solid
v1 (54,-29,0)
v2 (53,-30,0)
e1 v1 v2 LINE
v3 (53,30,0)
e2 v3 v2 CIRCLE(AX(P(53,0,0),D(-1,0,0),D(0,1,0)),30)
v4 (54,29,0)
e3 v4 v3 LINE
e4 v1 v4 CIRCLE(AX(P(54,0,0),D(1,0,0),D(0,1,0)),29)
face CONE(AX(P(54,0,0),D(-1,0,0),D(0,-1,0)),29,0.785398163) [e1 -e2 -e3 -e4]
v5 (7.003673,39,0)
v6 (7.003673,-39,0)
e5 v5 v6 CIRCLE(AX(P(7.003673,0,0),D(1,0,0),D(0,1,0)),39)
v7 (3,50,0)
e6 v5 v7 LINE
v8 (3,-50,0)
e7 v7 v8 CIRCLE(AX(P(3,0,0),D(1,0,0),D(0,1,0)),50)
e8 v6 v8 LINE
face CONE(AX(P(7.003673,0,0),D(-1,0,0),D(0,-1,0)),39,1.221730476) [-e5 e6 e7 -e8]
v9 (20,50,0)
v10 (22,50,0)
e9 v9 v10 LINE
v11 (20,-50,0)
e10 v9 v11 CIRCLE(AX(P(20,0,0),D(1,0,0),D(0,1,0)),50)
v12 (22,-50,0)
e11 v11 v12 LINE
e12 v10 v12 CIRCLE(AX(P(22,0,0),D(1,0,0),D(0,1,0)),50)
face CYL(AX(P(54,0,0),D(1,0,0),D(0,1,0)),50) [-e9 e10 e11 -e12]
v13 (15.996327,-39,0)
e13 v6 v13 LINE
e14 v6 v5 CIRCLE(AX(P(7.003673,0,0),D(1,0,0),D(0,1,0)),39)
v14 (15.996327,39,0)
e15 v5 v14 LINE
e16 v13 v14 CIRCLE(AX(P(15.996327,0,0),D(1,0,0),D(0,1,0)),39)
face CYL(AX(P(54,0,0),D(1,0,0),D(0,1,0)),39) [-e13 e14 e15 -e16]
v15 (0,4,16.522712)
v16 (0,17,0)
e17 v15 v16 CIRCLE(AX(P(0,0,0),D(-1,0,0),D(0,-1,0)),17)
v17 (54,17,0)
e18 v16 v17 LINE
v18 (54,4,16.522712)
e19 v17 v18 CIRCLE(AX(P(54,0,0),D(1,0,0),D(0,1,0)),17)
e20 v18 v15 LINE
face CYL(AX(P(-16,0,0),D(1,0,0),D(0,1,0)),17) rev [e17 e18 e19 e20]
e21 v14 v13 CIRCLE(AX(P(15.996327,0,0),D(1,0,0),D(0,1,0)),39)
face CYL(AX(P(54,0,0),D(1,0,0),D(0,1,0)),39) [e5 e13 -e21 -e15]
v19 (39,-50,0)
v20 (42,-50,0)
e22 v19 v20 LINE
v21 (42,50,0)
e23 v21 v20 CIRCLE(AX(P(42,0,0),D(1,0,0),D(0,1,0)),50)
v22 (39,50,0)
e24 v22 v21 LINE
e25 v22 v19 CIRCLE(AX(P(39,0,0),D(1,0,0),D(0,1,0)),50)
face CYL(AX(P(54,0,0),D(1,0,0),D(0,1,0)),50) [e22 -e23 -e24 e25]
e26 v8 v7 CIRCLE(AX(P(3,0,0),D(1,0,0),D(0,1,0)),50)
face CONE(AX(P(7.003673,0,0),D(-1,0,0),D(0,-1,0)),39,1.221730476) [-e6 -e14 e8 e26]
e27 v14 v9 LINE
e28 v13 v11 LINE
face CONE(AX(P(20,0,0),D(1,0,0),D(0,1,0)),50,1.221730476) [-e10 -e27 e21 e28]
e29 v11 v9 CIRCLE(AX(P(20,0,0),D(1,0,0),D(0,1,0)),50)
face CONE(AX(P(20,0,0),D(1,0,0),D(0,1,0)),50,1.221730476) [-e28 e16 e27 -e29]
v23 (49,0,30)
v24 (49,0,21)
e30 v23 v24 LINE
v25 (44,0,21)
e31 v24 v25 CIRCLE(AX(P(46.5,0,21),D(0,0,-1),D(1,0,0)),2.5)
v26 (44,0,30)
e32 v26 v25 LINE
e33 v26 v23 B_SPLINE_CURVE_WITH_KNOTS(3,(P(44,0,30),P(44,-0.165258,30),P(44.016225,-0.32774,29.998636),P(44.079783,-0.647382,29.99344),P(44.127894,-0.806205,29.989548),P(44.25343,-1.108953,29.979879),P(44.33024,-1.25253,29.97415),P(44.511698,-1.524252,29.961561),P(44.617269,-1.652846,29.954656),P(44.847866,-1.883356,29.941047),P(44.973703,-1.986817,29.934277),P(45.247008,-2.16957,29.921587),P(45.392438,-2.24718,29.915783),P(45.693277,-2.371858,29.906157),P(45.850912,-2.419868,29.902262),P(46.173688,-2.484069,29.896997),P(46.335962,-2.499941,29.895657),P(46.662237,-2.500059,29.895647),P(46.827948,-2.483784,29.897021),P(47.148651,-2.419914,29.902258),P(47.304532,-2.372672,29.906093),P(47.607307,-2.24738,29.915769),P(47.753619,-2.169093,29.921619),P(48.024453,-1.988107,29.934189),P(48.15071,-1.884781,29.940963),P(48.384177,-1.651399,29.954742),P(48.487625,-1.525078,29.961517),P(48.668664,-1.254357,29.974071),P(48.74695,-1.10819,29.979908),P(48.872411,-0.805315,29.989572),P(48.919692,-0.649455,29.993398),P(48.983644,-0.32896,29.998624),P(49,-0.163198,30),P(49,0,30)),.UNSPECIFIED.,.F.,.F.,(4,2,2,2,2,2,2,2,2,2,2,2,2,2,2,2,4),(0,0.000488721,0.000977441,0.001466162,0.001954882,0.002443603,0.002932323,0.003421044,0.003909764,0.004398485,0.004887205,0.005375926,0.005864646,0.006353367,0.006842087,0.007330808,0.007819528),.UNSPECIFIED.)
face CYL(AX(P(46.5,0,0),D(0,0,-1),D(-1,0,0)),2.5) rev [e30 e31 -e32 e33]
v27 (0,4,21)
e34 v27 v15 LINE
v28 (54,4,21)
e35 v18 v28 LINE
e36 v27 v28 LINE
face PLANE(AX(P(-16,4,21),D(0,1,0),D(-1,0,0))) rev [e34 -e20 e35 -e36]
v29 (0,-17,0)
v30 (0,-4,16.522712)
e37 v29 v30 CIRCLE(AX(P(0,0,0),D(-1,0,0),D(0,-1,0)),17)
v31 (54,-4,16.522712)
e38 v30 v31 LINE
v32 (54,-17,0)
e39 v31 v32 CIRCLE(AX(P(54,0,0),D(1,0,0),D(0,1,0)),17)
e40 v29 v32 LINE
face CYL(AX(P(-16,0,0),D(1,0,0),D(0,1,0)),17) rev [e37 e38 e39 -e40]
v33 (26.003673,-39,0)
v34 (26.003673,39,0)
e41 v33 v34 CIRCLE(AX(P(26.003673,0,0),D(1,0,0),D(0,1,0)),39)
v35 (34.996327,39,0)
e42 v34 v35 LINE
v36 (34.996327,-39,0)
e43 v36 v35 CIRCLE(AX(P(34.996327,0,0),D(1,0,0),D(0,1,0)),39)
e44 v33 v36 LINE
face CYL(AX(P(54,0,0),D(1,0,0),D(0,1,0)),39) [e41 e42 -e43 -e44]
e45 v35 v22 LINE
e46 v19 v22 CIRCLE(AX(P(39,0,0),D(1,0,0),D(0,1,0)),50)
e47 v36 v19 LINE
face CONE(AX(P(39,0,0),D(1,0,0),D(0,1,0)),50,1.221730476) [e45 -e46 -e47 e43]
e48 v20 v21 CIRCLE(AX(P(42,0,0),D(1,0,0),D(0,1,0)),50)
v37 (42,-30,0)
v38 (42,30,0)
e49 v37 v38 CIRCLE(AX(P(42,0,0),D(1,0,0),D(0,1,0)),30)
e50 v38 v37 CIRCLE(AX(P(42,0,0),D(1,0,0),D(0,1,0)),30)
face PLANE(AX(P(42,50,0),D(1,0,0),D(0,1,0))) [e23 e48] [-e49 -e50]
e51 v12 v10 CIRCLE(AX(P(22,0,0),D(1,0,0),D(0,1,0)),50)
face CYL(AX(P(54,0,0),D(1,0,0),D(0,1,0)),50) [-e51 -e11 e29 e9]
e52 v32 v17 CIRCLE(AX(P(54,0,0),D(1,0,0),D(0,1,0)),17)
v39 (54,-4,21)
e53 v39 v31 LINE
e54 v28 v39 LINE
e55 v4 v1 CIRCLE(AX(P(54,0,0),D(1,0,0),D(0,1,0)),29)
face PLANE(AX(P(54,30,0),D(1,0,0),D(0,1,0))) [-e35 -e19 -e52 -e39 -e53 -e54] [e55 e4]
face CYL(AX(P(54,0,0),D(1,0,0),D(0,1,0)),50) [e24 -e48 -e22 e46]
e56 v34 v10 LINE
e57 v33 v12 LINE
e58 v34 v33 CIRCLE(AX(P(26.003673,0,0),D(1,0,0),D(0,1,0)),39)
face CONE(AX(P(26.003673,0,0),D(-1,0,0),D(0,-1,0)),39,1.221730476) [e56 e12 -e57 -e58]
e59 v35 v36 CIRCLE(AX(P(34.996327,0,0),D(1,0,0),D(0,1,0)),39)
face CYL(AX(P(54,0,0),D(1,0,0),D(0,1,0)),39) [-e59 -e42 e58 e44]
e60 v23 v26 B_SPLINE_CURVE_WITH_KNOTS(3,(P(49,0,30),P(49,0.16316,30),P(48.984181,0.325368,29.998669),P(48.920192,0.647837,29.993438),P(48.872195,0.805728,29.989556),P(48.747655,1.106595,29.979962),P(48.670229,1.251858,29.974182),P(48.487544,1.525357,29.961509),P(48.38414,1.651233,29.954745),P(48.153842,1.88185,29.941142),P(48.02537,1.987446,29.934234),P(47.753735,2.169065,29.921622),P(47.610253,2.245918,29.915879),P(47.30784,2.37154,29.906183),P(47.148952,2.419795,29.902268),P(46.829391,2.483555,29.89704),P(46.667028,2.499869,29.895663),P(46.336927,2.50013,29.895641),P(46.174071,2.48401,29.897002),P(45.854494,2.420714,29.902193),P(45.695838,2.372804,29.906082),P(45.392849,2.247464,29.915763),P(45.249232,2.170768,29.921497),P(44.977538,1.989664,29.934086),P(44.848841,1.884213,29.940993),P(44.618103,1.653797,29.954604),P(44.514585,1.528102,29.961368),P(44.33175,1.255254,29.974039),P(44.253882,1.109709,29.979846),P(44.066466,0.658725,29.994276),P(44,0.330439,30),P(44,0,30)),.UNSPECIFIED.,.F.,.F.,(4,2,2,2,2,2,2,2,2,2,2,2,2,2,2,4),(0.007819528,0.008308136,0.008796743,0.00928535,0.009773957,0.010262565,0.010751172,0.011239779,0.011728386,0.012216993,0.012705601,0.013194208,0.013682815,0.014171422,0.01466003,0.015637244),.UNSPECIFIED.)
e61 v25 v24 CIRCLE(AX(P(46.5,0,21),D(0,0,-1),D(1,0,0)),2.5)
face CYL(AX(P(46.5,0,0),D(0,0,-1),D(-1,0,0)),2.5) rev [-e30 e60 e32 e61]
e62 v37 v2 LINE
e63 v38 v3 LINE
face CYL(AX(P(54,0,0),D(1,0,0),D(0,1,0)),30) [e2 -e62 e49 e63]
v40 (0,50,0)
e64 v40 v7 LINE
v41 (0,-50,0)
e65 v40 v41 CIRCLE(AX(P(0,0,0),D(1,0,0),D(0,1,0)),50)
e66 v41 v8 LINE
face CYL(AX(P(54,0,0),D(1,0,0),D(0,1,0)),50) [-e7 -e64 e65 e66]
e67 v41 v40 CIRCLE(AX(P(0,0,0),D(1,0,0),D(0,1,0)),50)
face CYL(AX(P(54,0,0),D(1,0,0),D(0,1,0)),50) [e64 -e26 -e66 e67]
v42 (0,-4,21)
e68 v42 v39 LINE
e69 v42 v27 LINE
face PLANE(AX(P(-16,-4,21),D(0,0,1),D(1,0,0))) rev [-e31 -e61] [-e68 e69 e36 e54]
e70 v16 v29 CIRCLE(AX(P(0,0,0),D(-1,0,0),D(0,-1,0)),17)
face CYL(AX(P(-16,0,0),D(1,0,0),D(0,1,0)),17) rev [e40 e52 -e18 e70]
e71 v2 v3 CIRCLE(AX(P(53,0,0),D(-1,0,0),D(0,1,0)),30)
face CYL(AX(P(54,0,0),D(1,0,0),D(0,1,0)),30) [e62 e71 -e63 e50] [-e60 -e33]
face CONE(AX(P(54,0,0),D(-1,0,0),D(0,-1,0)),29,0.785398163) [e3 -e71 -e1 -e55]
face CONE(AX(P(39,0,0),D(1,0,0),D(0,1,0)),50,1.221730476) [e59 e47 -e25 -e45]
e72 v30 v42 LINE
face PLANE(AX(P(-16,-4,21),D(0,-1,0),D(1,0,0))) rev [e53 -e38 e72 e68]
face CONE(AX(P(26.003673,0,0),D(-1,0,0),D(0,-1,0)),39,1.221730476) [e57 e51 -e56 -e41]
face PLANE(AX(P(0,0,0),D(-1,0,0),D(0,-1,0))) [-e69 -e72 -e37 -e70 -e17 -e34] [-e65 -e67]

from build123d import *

# Parameters (mm, degrees)
SKETCH2_R          = 17
CUT_EXTRUDE1_DEPTH = 70
CHAMFER1_SIZE      = 1
SKETCH7_W          = 8
SKETCH7_H          = 8
CUT_EXTRUDE2_DEPTH = 70


with BuildPart() as part:
    # Sketch1 → Revolve1 (revolve)
    with BuildSketch(Plane.XY):
        Polygon((0, 0), (0, 50), (3, 50), (7.003672577, 39), (15.996327423, 39), (20, 50), (22, 50), (26.003672577, 39), (34.996327423, 39), (39, 50), (42, 50), (42, 30), (54, 30), (54, 0), align=None)
    revolve(axis=Axis((54, 0, 0), (-1, 0, 0)))

    # Sketch2 → Cut-Extrude1 (cut)
    with BuildSketch(Plane(origin=(54, 0, 0), x_dir=(0, 0, -1), z_dir=(1, 0, 0))):
        with Locations(Location((0, 0, 0), (0, 0, 90))):
            Circle(SKETCH2_R)
    extrude(amount=-CUT_EXTRUDE1_DEPTH, mode=Mode.SUBTRACT)

    # Sketch5 → M6 Tapped Hole1 (revolve, cut)
    with BuildSketch(Plane.YZ.offset(46.5)):
        Polygon((0, 0), (0, 51.502151548), (2.5, 50), (2.5, 0), align=None)
    revolve(axis=Axis((46.5, 0, -6.35), (0, 0, 1)), mode=Mode.SUBTRACT)

    # Chamfer1
    chamfer1_edges = [part.edges().sort_by_distance(p)[0] for p in [
        (54, -30, 0),
    ]]
    chamfer(chamfer1_edges, length=CHAMFER1_SIZE)

    # Sketch7 → Cut-Extrude2 (cut)
    with BuildSketch(Plane(origin=(54, 0, 0), x_dir=(0, 0, -1), z_dir=(1, 0, 0))):
        with Locations((-17, 0)):
            Rectangle(SKETCH7_W, SKETCH7_H)
    extrude(amount=-CUT_EXTRUDE2_DEPTH, mode=Mode.SUBTRACT)


solid = part.part
